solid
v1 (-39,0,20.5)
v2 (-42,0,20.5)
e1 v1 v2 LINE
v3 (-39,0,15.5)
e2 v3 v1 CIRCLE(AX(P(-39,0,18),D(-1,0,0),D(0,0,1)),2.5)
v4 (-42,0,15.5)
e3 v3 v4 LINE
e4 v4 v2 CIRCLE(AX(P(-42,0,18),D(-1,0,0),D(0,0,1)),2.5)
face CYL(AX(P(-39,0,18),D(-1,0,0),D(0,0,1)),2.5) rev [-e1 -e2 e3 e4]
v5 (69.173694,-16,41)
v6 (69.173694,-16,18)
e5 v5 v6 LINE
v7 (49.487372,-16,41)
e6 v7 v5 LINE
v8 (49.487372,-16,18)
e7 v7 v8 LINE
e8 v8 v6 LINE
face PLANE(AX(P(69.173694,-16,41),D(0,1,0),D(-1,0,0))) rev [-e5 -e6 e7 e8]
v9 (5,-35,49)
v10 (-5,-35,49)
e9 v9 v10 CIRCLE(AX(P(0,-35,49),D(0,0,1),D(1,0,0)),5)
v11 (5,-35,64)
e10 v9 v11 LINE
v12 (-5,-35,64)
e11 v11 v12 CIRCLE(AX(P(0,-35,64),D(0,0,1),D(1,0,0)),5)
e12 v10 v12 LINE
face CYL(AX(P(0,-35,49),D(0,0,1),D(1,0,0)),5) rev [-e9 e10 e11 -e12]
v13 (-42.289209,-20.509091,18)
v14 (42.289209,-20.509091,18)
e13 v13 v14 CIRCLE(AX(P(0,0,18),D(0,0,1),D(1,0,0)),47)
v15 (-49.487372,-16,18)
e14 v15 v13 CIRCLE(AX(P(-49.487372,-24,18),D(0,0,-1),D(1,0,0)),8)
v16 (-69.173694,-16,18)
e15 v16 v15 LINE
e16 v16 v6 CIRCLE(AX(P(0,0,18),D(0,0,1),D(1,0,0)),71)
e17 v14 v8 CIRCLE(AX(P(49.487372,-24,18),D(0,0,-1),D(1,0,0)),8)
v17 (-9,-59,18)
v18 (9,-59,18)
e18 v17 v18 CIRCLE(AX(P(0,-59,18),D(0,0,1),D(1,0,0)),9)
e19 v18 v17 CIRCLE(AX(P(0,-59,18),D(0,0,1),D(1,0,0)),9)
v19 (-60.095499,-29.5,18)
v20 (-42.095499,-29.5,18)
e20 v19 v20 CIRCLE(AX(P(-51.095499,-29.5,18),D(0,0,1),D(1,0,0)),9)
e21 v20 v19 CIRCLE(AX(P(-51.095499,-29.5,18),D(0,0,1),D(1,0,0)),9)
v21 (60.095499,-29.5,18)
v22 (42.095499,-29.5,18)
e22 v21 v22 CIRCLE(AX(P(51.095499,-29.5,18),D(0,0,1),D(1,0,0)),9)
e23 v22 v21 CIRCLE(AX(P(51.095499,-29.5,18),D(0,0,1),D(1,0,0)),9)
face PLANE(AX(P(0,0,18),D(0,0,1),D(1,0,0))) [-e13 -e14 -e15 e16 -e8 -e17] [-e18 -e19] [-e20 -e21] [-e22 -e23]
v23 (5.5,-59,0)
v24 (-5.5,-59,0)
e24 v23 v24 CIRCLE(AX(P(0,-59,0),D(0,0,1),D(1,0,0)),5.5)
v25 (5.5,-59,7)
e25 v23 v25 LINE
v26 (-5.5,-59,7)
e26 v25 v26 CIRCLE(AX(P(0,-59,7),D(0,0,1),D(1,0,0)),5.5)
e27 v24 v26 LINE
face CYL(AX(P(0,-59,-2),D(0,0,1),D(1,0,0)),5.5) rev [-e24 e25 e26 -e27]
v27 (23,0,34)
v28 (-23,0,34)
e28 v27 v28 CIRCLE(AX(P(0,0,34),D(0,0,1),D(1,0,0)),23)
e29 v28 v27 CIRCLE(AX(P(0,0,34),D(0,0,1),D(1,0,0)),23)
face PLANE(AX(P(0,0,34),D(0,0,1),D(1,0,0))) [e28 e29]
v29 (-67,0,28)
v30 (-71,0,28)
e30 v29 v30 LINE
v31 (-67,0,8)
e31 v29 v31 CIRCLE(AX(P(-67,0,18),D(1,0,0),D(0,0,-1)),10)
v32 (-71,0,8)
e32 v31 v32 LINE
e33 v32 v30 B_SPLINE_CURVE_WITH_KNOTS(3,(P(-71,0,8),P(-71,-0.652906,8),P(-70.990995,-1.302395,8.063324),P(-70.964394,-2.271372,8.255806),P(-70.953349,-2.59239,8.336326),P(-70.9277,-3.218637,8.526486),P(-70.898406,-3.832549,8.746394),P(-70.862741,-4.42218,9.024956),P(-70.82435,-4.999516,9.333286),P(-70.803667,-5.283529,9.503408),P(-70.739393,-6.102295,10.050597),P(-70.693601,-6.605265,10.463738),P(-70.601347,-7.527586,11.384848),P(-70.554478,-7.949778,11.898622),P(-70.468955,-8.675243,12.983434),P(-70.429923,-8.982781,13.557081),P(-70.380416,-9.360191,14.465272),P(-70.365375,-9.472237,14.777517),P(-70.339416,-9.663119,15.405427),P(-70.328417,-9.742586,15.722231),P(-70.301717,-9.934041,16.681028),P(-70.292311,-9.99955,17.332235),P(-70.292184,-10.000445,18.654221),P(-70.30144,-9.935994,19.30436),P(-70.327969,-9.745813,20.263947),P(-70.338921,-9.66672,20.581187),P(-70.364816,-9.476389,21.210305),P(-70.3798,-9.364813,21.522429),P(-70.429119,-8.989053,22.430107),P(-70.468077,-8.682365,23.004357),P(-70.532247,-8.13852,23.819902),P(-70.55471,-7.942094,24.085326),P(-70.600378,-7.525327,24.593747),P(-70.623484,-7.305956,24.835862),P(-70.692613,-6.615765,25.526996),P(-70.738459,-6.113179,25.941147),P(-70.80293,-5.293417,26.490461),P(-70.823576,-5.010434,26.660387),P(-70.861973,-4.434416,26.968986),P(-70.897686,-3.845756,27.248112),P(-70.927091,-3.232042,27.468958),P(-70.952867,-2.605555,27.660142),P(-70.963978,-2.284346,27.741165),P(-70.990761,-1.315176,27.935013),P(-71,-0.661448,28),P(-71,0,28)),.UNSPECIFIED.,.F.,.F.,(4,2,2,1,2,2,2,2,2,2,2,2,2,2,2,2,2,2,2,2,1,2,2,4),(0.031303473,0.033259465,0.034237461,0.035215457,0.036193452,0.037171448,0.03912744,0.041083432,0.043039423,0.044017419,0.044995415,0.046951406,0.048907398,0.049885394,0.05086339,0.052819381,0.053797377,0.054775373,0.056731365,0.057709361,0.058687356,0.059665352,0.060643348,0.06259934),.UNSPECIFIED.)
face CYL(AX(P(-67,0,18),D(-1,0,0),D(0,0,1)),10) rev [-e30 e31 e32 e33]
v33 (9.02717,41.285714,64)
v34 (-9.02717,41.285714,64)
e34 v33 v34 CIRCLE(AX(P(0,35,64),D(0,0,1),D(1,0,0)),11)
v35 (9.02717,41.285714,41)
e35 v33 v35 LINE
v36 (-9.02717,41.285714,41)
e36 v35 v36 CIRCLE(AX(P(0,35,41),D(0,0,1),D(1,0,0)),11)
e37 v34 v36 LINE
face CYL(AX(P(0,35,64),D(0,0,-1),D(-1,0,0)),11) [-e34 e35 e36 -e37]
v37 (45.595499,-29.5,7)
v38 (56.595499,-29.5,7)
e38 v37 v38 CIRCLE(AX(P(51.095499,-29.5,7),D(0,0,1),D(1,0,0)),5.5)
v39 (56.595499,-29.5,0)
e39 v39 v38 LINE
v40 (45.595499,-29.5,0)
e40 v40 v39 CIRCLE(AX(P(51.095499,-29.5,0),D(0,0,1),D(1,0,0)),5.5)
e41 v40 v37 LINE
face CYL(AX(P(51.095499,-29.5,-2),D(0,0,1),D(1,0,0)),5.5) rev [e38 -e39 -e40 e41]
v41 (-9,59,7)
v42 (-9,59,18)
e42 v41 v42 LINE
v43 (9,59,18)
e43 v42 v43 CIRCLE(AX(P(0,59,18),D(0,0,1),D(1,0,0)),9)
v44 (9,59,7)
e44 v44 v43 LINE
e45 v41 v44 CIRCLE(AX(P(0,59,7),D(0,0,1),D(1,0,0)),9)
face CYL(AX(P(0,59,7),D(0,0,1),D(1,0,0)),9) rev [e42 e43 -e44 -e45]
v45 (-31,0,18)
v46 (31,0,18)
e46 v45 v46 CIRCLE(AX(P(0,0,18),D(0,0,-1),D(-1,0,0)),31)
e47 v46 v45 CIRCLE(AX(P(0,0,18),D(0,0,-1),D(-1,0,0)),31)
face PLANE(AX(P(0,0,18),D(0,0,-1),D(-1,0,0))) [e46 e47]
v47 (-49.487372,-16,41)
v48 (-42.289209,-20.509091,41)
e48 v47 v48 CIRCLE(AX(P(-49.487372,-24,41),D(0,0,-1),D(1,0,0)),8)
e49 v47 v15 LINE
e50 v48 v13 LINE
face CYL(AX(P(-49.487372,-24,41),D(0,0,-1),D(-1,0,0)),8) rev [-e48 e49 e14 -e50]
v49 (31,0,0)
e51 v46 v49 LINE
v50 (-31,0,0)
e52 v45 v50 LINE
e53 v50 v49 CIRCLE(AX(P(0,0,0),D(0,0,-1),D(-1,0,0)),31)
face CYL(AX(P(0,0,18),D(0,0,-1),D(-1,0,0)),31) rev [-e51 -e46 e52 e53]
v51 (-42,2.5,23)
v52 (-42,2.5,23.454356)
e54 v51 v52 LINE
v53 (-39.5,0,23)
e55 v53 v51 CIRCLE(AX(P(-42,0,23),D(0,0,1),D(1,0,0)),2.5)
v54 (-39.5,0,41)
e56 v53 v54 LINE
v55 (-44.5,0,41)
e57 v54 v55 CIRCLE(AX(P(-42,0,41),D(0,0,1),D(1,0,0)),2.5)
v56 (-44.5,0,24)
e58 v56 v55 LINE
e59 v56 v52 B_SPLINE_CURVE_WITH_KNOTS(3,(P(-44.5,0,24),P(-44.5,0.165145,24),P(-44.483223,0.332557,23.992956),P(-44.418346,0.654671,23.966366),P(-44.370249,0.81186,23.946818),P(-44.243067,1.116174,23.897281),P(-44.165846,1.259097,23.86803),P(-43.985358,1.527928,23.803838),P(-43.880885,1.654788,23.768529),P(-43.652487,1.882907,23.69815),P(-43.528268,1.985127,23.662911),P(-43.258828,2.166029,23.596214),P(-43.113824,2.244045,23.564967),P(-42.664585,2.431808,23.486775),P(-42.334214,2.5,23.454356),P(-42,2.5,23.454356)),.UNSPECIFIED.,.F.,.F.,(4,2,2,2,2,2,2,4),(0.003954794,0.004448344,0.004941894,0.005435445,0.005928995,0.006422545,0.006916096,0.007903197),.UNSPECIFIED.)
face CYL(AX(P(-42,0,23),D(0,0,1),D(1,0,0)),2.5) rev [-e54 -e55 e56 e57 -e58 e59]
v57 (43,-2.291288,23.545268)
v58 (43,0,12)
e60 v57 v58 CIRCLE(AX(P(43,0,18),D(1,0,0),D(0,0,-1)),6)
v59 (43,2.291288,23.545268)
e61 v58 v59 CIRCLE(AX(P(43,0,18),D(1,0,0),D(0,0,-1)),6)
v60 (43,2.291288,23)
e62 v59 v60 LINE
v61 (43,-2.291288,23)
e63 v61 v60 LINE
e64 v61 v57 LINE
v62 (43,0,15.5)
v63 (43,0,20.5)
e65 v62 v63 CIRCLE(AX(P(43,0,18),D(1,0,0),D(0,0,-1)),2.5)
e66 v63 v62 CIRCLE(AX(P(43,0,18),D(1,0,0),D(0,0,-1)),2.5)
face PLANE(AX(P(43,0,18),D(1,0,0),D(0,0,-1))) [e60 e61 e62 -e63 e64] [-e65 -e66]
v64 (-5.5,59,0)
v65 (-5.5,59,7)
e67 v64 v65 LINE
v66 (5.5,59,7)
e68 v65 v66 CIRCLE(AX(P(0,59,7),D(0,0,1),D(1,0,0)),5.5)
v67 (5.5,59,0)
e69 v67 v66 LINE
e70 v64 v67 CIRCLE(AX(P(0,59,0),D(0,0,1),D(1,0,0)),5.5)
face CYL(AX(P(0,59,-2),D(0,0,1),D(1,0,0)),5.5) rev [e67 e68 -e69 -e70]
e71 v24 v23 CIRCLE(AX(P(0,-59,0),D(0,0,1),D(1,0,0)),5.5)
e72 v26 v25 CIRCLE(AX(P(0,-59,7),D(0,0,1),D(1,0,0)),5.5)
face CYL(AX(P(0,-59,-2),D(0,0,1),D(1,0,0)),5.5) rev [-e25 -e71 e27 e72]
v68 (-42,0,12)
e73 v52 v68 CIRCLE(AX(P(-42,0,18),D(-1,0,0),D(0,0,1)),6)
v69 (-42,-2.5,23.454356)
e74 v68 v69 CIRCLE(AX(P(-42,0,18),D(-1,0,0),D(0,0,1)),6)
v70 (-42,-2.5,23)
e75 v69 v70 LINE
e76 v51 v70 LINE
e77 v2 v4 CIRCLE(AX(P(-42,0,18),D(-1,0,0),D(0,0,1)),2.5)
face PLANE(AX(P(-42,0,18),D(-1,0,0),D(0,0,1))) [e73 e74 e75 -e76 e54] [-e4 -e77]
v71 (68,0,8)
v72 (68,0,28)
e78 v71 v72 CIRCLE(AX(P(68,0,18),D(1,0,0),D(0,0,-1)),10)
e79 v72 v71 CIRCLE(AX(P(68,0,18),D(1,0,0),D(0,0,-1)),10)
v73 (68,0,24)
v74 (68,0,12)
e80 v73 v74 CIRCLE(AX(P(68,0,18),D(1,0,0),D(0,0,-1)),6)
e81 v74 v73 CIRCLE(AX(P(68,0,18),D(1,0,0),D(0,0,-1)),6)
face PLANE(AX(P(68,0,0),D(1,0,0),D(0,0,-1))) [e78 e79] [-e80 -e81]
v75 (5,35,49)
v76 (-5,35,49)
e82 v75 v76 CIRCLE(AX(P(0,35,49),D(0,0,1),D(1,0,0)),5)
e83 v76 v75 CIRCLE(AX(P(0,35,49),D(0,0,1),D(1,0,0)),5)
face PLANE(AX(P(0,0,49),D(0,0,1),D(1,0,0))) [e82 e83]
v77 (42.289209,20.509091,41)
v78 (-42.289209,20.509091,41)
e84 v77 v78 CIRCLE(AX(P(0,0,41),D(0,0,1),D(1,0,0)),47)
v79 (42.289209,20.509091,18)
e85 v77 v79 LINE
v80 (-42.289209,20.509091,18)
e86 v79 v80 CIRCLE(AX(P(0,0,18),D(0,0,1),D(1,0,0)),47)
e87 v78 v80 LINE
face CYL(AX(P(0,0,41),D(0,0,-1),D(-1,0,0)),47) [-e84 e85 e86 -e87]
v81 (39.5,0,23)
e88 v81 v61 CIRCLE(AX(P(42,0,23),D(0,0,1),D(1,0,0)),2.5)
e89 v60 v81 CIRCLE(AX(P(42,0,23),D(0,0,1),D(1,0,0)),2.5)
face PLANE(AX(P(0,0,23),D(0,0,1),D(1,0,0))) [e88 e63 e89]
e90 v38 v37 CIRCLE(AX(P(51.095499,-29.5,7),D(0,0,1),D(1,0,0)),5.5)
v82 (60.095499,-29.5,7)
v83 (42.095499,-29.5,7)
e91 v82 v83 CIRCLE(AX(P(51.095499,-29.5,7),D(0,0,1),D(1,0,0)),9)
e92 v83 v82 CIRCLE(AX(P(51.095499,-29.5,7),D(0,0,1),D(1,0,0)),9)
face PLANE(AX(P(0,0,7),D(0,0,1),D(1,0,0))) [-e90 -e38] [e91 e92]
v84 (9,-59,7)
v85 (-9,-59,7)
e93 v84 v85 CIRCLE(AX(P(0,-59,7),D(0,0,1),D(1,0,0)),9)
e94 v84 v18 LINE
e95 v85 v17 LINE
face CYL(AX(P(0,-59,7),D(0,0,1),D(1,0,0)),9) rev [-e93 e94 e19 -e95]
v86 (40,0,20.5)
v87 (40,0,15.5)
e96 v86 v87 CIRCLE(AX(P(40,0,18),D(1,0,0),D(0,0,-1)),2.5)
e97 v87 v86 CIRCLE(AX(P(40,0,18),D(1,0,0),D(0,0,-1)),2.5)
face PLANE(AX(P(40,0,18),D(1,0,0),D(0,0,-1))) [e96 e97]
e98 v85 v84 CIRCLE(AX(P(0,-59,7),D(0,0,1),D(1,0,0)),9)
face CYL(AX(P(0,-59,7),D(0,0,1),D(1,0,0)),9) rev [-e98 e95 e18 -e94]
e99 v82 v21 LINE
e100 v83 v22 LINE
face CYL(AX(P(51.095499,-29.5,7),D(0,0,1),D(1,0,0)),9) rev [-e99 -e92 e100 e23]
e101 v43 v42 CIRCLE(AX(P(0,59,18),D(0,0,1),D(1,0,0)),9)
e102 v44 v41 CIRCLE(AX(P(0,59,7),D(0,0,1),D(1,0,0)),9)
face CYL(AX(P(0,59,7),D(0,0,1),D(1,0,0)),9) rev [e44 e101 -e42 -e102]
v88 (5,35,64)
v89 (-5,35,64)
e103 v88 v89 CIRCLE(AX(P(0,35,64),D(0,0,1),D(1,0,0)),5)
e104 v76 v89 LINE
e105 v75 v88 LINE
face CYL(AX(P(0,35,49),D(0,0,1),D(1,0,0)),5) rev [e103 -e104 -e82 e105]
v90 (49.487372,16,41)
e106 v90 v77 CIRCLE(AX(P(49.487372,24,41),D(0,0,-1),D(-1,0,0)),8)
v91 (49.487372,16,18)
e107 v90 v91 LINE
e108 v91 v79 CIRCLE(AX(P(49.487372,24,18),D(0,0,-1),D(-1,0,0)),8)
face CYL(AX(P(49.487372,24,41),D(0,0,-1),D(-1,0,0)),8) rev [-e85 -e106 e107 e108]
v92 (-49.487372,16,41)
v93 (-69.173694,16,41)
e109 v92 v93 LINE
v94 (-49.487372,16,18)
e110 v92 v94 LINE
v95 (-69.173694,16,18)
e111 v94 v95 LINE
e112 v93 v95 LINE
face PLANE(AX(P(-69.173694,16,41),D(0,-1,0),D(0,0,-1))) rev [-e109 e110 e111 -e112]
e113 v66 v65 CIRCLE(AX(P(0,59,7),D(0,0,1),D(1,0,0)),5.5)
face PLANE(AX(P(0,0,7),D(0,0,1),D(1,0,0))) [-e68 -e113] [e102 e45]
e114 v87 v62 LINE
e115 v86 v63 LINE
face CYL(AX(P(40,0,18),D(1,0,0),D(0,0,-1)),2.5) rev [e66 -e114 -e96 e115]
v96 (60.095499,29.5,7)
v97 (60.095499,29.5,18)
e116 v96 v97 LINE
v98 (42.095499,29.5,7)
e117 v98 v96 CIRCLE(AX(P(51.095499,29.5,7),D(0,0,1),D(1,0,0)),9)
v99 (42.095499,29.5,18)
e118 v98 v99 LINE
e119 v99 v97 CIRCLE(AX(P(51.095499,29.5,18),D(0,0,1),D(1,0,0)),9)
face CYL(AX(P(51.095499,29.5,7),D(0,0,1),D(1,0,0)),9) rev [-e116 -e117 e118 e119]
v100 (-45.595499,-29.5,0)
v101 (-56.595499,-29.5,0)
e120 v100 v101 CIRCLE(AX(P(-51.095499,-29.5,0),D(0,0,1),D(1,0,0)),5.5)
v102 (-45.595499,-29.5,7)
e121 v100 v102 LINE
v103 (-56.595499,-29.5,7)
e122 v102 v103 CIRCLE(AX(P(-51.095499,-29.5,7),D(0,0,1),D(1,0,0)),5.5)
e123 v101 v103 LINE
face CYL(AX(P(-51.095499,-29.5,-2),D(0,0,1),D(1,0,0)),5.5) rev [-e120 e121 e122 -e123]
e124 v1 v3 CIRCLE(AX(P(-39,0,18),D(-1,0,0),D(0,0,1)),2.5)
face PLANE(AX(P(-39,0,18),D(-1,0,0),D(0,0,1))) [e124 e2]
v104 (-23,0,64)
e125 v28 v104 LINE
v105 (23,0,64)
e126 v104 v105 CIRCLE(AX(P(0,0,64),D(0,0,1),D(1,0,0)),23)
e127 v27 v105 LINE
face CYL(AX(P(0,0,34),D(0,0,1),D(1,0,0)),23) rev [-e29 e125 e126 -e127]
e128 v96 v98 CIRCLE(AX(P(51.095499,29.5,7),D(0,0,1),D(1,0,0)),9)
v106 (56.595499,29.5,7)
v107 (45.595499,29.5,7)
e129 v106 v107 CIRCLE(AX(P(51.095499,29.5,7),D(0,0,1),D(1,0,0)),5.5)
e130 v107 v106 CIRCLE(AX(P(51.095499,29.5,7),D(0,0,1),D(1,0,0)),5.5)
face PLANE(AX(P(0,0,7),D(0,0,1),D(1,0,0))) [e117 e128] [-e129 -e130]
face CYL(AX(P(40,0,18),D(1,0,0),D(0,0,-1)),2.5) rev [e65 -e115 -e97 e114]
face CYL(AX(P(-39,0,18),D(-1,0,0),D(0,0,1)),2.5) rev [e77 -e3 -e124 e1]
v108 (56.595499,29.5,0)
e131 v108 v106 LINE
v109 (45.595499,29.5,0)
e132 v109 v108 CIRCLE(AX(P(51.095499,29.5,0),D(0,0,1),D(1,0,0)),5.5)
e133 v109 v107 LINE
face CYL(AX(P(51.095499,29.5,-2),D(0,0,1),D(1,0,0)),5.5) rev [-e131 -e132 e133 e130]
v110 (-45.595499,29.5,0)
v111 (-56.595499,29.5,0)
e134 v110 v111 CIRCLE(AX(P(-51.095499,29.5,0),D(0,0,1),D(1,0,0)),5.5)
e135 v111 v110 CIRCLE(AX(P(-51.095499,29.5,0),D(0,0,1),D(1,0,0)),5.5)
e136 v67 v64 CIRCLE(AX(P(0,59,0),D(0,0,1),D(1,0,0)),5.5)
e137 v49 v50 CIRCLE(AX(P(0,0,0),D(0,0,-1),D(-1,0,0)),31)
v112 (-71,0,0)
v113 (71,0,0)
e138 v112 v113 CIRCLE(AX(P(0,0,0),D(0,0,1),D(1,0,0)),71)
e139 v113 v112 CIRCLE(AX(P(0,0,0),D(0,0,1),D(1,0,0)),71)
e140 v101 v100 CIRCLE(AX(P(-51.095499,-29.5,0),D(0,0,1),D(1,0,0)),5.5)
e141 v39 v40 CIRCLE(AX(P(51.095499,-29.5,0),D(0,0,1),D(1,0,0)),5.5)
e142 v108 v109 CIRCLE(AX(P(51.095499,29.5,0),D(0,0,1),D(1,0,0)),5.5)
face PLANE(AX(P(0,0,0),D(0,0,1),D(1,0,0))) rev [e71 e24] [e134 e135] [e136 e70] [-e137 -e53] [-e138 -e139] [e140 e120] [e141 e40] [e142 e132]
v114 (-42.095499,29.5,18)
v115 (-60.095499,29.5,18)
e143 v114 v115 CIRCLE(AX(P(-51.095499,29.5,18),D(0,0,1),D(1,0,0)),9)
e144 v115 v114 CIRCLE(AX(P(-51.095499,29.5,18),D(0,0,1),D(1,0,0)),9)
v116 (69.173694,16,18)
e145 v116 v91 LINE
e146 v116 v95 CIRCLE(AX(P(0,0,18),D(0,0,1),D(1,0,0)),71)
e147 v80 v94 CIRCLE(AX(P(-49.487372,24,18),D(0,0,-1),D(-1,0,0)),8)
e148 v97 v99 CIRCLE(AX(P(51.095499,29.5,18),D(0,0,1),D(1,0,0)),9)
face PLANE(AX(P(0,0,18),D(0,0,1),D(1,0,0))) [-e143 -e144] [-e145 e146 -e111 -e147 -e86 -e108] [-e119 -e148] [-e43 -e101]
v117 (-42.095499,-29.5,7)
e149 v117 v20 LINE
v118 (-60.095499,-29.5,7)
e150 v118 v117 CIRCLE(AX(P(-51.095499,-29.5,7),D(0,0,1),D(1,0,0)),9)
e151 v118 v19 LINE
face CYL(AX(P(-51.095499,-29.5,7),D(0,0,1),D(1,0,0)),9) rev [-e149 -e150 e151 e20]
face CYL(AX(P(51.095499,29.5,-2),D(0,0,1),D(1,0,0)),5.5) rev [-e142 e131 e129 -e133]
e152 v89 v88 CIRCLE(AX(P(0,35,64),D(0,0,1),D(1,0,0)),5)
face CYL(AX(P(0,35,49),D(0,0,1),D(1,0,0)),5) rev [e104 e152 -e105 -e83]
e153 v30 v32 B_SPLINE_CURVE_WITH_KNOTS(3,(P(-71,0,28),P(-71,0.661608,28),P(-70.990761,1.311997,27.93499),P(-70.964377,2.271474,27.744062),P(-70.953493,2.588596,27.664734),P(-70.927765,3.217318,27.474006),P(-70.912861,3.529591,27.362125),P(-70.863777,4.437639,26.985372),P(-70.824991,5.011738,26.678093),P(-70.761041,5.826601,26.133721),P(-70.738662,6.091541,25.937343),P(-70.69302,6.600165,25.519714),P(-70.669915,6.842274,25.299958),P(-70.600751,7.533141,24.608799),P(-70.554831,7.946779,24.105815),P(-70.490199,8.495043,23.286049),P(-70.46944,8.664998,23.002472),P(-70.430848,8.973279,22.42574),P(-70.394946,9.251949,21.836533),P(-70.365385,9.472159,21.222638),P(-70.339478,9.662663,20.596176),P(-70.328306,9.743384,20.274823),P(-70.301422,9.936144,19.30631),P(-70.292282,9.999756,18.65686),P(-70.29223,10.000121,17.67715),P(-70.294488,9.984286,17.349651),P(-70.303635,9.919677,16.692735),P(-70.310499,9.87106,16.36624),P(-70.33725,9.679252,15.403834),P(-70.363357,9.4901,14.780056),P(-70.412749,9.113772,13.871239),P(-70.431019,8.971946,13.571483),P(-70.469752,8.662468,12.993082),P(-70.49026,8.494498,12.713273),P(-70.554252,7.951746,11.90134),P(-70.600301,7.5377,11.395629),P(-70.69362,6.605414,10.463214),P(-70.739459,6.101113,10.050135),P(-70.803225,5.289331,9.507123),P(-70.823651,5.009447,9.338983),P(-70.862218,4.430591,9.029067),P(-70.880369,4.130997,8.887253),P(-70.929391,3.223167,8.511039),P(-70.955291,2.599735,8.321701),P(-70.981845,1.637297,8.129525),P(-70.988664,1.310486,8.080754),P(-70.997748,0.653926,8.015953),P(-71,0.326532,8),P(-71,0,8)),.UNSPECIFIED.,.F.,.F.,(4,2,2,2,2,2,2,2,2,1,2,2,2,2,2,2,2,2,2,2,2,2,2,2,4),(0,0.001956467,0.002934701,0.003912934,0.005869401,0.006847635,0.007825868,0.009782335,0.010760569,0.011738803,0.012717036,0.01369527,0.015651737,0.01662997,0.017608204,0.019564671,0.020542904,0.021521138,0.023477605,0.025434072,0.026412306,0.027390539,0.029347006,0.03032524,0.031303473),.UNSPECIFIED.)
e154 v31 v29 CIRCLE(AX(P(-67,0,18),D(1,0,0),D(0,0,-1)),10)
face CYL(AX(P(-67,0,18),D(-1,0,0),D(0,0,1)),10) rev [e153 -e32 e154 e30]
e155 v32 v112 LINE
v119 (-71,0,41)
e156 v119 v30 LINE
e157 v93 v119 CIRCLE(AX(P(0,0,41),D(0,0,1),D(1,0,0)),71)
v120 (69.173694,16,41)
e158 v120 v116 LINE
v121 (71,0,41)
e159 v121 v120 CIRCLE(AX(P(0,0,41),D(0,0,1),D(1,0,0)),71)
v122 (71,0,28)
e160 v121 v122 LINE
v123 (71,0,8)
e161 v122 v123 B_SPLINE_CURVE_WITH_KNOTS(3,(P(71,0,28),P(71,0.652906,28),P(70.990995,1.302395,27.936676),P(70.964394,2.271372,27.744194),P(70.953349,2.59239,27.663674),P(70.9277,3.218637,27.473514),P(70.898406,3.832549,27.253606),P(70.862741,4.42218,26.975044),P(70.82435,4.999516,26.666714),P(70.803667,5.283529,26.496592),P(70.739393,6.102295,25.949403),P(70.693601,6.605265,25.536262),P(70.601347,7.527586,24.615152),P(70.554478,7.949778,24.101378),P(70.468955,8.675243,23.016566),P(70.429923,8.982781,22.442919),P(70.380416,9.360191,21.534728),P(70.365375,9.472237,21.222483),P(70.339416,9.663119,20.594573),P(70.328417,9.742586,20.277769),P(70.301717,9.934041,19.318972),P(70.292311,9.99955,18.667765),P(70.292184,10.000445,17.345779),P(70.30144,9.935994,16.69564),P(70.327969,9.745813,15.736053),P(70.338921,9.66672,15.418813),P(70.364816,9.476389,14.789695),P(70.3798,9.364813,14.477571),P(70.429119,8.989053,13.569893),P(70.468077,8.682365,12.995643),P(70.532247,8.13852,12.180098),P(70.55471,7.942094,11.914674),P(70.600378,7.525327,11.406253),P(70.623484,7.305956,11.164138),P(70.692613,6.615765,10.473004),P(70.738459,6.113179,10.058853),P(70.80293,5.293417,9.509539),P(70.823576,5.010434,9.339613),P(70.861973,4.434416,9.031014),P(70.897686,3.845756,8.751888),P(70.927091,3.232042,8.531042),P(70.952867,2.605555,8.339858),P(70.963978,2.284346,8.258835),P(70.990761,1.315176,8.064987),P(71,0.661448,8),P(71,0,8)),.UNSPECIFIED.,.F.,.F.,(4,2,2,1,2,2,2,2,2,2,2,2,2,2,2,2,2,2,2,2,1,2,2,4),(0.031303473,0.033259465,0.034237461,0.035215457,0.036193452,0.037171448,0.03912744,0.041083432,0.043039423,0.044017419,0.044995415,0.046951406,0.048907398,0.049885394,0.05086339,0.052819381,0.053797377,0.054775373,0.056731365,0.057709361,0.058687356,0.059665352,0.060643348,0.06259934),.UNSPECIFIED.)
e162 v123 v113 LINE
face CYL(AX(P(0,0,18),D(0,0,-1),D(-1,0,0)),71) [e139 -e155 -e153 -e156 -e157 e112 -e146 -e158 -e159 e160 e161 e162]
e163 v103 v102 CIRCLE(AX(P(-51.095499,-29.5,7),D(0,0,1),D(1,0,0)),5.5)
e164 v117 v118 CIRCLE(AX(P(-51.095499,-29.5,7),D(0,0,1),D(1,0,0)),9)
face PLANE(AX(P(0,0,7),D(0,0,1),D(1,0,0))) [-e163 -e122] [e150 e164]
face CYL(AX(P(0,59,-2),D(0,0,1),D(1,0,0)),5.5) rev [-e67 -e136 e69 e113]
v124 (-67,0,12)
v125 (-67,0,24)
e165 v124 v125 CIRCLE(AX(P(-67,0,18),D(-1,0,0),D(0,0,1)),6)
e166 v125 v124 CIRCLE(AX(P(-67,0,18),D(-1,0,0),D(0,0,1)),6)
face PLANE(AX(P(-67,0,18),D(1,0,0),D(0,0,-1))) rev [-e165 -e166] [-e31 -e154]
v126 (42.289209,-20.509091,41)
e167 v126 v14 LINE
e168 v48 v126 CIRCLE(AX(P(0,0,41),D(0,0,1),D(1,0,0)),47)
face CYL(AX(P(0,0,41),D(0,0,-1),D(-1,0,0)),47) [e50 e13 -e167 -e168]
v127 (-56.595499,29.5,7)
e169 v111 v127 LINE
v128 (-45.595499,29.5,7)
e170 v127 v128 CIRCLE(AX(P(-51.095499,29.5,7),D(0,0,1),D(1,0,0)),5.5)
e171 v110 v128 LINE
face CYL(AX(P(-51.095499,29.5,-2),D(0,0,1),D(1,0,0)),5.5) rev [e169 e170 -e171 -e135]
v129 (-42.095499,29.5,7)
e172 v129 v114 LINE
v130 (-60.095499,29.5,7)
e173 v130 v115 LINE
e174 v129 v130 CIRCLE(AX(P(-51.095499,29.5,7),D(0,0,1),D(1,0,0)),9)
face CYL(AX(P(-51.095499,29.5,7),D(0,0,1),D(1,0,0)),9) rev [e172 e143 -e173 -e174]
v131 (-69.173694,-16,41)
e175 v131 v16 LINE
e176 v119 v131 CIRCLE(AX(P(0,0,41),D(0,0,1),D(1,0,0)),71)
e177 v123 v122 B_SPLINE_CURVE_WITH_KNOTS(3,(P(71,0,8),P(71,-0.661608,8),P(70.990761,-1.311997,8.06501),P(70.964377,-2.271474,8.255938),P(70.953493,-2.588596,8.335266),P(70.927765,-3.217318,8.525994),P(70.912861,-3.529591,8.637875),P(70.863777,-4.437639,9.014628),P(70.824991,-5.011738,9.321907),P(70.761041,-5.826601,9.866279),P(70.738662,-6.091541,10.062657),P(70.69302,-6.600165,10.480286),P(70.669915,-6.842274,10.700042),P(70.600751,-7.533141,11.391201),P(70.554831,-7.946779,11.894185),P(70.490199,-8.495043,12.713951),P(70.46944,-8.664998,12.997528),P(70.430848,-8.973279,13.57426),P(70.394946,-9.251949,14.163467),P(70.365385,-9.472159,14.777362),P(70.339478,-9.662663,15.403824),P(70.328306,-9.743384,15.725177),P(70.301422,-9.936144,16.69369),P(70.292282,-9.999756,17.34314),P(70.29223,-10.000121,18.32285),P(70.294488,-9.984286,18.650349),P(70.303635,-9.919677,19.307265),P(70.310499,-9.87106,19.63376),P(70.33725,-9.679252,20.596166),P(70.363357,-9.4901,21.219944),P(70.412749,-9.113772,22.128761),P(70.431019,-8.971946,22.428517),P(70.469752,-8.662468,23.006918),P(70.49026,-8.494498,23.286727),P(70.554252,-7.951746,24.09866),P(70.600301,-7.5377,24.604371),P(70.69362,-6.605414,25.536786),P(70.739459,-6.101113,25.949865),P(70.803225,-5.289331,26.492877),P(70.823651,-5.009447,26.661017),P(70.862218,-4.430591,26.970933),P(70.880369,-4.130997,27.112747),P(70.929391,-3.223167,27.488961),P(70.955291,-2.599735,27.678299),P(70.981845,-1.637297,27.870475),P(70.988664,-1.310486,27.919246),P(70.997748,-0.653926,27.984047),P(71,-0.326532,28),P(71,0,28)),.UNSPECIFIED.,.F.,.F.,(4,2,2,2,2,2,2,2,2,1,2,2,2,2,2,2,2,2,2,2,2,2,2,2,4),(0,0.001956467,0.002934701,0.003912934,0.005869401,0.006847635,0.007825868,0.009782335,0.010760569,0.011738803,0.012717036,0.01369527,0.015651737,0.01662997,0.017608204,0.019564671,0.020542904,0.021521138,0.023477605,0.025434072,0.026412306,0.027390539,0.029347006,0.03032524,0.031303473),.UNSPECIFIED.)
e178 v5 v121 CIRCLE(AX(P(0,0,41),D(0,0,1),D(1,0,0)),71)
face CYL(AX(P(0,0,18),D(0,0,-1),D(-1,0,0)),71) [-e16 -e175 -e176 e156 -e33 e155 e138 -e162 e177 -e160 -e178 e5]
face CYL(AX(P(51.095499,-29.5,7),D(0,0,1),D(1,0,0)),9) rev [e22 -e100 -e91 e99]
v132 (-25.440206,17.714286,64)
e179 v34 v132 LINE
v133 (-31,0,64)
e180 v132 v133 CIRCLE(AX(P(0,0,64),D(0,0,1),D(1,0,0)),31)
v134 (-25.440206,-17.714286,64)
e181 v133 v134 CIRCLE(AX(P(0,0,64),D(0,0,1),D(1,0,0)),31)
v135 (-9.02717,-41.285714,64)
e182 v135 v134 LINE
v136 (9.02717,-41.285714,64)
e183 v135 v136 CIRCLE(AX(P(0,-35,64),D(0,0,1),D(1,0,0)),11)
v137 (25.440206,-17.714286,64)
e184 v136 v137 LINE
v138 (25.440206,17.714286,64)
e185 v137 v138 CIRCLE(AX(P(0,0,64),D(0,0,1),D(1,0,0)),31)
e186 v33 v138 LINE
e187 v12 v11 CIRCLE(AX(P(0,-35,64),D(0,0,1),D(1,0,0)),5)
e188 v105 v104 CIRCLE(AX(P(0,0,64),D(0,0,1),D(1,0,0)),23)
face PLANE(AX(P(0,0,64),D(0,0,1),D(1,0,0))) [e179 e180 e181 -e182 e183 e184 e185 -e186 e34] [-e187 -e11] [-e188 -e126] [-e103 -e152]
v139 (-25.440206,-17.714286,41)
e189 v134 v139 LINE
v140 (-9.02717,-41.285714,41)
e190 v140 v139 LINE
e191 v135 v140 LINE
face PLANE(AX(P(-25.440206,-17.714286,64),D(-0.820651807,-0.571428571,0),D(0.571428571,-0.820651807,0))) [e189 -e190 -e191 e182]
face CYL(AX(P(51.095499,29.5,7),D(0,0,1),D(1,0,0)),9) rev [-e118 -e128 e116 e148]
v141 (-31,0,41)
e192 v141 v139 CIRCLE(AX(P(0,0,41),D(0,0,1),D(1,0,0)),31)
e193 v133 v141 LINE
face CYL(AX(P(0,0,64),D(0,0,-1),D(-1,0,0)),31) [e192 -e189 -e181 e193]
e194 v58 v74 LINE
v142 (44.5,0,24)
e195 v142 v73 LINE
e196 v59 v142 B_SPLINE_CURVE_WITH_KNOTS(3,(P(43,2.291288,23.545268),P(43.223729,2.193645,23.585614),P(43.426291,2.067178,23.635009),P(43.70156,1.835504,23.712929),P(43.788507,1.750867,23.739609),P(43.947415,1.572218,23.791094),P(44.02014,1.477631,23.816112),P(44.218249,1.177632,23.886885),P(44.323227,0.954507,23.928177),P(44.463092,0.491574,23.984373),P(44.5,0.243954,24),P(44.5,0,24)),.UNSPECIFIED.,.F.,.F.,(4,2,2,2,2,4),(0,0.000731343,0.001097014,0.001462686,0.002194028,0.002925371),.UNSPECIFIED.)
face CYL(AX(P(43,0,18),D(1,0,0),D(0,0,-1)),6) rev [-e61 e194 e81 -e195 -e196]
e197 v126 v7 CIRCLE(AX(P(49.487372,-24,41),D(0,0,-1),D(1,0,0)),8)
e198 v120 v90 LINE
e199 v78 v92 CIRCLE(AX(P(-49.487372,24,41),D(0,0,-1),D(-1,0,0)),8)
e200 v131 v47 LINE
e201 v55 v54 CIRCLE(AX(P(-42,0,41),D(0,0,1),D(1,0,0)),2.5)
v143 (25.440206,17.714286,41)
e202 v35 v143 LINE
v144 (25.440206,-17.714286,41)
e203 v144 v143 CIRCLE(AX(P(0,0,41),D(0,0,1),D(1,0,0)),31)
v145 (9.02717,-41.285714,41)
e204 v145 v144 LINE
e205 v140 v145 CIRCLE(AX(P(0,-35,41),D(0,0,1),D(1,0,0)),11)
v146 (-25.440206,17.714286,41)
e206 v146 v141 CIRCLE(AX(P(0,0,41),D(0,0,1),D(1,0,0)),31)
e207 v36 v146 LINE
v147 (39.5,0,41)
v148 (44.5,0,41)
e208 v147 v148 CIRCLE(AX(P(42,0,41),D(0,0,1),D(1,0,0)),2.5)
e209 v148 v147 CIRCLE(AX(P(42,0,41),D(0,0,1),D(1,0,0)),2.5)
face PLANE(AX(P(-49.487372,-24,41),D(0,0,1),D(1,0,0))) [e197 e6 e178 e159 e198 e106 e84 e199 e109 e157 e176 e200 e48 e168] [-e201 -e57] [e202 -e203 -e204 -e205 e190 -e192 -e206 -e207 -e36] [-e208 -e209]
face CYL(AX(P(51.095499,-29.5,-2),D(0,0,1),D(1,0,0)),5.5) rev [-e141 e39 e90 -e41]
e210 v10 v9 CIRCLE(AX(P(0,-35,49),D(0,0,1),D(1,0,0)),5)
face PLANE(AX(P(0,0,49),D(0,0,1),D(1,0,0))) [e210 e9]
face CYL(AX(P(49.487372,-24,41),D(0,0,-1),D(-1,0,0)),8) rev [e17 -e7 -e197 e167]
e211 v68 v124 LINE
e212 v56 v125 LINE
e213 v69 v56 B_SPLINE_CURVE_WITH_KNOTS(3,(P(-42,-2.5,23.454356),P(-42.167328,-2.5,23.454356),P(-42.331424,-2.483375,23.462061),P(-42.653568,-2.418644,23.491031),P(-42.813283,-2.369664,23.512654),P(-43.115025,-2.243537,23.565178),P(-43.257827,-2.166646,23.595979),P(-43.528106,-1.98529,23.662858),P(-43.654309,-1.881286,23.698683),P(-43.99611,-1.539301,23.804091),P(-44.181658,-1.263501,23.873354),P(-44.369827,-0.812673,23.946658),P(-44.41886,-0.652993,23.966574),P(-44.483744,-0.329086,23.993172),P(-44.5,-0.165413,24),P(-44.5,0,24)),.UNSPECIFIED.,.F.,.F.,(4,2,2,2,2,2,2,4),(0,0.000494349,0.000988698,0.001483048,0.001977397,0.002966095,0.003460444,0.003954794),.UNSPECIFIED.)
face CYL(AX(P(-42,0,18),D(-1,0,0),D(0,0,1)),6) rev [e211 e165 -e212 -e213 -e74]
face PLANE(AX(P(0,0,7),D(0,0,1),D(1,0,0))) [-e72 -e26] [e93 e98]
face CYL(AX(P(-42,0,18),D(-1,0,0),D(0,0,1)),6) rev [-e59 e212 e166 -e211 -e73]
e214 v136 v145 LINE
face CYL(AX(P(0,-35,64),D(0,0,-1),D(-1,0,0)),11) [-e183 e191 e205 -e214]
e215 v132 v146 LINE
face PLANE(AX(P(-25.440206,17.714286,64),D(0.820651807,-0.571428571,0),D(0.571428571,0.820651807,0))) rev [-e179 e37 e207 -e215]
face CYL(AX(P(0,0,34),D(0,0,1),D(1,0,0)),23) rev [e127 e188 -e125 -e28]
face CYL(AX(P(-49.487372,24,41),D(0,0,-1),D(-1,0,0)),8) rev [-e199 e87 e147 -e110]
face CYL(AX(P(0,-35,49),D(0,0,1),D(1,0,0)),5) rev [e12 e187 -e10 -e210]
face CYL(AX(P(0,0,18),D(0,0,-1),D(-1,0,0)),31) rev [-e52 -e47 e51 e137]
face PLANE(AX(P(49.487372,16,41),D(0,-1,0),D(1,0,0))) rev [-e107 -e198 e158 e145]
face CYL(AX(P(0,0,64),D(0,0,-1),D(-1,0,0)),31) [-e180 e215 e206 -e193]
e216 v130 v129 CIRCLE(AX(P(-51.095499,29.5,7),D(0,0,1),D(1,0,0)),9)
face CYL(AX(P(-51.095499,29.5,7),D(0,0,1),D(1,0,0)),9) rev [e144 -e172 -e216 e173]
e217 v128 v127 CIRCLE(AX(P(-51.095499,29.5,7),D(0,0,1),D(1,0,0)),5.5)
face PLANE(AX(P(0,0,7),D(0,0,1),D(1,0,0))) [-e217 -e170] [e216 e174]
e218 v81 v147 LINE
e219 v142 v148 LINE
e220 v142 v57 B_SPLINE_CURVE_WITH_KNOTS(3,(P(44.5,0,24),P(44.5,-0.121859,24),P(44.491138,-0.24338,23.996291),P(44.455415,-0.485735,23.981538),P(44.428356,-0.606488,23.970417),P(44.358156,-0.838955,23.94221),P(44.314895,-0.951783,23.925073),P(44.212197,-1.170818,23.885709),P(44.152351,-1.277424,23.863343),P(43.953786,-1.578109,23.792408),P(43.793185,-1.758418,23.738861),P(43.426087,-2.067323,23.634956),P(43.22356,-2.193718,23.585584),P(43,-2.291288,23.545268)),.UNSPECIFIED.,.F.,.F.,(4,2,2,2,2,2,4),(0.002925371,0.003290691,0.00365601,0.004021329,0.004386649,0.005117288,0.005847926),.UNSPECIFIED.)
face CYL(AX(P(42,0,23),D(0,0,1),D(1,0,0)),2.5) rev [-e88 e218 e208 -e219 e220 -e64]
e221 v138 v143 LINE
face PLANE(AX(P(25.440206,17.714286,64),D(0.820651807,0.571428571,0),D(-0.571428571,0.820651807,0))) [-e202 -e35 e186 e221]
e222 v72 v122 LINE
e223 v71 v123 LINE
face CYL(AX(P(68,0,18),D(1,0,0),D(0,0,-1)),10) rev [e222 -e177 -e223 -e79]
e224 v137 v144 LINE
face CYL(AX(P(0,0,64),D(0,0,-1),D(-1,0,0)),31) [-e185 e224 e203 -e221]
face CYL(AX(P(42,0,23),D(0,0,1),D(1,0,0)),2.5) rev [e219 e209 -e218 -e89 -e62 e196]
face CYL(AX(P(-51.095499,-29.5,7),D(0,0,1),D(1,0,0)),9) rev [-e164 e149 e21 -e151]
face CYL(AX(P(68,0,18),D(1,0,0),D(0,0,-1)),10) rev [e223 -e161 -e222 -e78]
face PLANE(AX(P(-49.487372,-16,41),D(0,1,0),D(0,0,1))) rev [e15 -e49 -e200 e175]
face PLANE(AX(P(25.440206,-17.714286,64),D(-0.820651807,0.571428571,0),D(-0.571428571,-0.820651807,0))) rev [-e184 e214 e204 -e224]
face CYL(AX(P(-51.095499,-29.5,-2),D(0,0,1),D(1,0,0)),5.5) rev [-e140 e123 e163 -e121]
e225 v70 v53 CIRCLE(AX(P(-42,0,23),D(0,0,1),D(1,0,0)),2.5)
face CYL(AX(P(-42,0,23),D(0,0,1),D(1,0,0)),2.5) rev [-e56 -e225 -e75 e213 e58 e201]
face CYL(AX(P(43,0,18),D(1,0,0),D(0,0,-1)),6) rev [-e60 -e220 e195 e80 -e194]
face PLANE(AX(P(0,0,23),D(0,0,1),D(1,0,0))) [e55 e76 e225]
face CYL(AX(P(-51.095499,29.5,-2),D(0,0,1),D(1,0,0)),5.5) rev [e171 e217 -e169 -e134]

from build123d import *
from build123d.topology import SkipClean

# Parameters (mm, degrees)
FLANGE_SKETCH_R              = 71
FLANGE_142_DEPTH             = 18
BODY_BOSS_WITH_LUGS_DEPTH    = 23
FLANGE_COUNTERBORE_SKETCH_R  = 9
FLANGE_COUNTERBORES_6X_DEPTH = 11
FLANGE_HOLE_SKETCH_R         = 5.5
FLANGE_HOLES_6X_11_DEPTH     = 20
TOP_BOSS_DEPTH               = 23
BORE_SKETCH_R                = 23
BORE_46_DEPTH                = 30
TOP_BOSS_HOLE_SKETCH_R       = 5
TOP_BOSS_HOLES_DEPTH         = 15
THROUGH_BORE_SKETCH_R        = 31
THROUGH_BORE_62_DEPTH        = 18
BODY_BOSS_HOLE_SKETCH_R      = 2.5
BODY_BOSS_HOLES_DEPTH        = 18
LUG_A_SPOT_FACE_DEPTH        = 4
LUG_A_HOLE_12_SKETCH_R       = 6
LUG_A_HOLE_12_DEPTH          = 25
LUG_A_HOLE_5_SKETCH_R        = 2.5
LUG_A_HOLE_5_DEPTH           = 3
LUG_START                    = 4
LUG_B_SPOT_FACE_SKETCH_R     = 10
LUG_B_SPOT_FACE_DEPTH        = 4
LUG_START_2                  = -25
LUG_B_HOLE_12_SKETCH_R       = 6
LUG_B_HOLE_12_DEPTH          = 25
LUG_START_3                  = -3
LUG_B_HOLE_5_SKETCH_R        = 2.5
LUG_B_HOLE_5_DEPTH           = 3


with BuildPart() as part:
    # Flange Sketch → Flange Ø142 (new body)
    with BuildSketch(Plane.XY):
        Circle(FLANGE_SKETCH_R)
    extrude(amount=FLANGE_142_DEPTH)

    # Body Boss Sketch → Body Boss With Lugs (add)
    with SkipClean():  # the faces are left unmerged after this step: merging them gives an invalid solid
        with BuildSketch(Plane.XY.offset(18)):
            with BuildLine():
                Line((-69.173694422, 16), (-49.487372127, 16))
                ThreePointArc((-49.487372127, 16), (-45.240448106, 17.22035131), (-42.289208908, 20.509090909))
                ThreePointArc((-42.289208908, 20.509090909), (0, 47), (42.289208908, 20.509090909))
                ThreePointArc((42.289208908, 20.509090909), (45.240448106, 17.22035131), (49.487372127, 16))
                Line((49.487372127, 16), (69.173694422, 16))
                ThreePointArc((69.173694422, 16), (71, 0), (69.173694422, -16))
                Line((69.173694422, -16), (49.487372127, -16))
                ThreePointArc((49.487372127, -16), (45.240448106, -17.22035131), (42.289208908, -20.509090909))
                ThreePointArc((42.289208908, -20.509090909), (0, -47), (-42.289208908, -20.509090909))
                ThreePointArc((-42.289208908, -20.509090909), (-45.240448106, -17.22035131), (-49.487372127, -16))
                Line((-49.487372127, -16), (-69.173694422, -16))
                ThreePointArc((-69.173694422, -16), (-71, 0), (-69.173694422, 16))
            make_face()
        extrude(amount=BODY_BOSS_WITH_LUGS_DEPTH)

    # Flange Counterbore Sketch → Flange Counterbores 6x (cut)
    with SkipClean():  # the faces are left unmerged after this step: merging them gives an invalid solid
        with BuildSketch(Plane.XY.offset(18)):
            with Locations((0, 59)):
                Circle(FLANGE_COUNTERBORE_SKETCH_R)
            with Locations((51.095498823, 29.5)):
                Circle(FLANGE_COUNTERBORE_SKETCH_R)
            with Locations((51.095498823, -29.5)):
                Circle(FLANGE_COUNTERBORE_SKETCH_R)
            with Locations((0, -59)):
                Circle(FLANGE_COUNTERBORE_SKETCH_R)
            with Locations((-51.095498823, -29.5)):
                Circle(FLANGE_COUNTERBORE_SKETCH_R)
            with Locations((-51.095498823, 29.5)):
                Circle(FLANGE_COUNTERBORE_SKETCH_R)
        extrude(amount=-FLANGE_COUNTERBORES_6X_DEPTH, mode=Mode.SUBTRACT)

    # Flange Hole Sketch → Flange Holes 6xØ11 (cut)
    with SkipClean():  # the faces are left unmerged after this step: merging them gives an invalid solid
        with BuildSketch(Plane.XY.offset(18)):
            with Locations((0, 59)):
                Circle(FLANGE_HOLE_SKETCH_R)
            with Locations((51.095498823, 29.5)):
                Circle(FLANGE_HOLE_SKETCH_R)
            with Locations((51.095498823, -29.5)):
                Circle(FLANGE_HOLE_SKETCH_R)
            with Locations((0, -59)):
                Circle(FLANGE_HOLE_SKETCH_R)
            with Locations((-51.095498823, -29.5)):
                Circle(FLANGE_HOLE_SKETCH_R)
            with Locations((-51.095498823, 29.5)):
                Circle(FLANGE_HOLE_SKETCH_R)
        extrude(amount=-FLANGE_HOLES_6X_11_DEPTH, mode=Mode.SUBTRACT)

    # Top Boss Sketch → Top Boss (add)
    with SkipClean():  # the faces are left unmerged after this step: merging them gives an invalid solid
        with BuildSketch(Plane.XY.offset(41)):
            with BuildLine():
                Line((9.027169873, -41.285714286), (25.440206006, -17.714285714))
                ThreePointArc((25.440206006, -17.714285714), (31, 0), (25.440206006, 17.714285714))
                Line((25.440206006, 17.714285714), (9.027169873, 41.285714286))
                ThreePointArc((9.027169873, 41.285714286), (0, 46), (-9.027169873, 41.285714286))
                Line((-9.027169873, 41.285714286), (-25.440206006, 17.714285714))
                ThreePointArc((-25.440206006, 17.714285714), (-31, 0), (-25.440206006, -17.714285714))
                Line((-25.440206006, -17.714285714), (-9.027169873, -41.285714286))
                ThreePointArc((-9.027169873, -41.285714286), (0, -46), (9.027169873, -41.285714286))
            make_face()
        extrude(amount=TOP_BOSS_DEPTH)

    # Bore Sketch → Bore Ø46 (cut)
    with SkipClean():  # the faces are left unmerged after this step: merging them gives an invalid solid
        with BuildSketch(Plane.XY.offset(64)):
            Circle(BORE_SKETCH_R)
        extrude(amount=-BORE_46_DEPTH, mode=Mode.SUBTRACT)

    # Top Boss Hole Sketch → Top Boss Holes (cut)
    with SkipClean():  # the faces are left unmerged after this step: merging them gives an invalid solid
        with BuildSketch(Plane.XY.offset(64)):
            with Locations((0, 35)):
                Circle(TOP_BOSS_HOLE_SKETCH_R)
            with Locations((0, -35)):
                Circle(TOP_BOSS_HOLE_SKETCH_R)
        extrude(amount=-TOP_BOSS_HOLES_DEPTH, mode=Mode.SUBTRACT)

    # Through Bore Sketch → Through Bore Ø62 (cut)
    with SkipClean():  # the faces are left unmerged after this step: merging them gives an invalid solid
        with BuildSketch(Plane(origin=(0, 0, 0), x_dir=(-1, 0, 0), z_dir=(0, 0, -1))):
            Circle(THROUGH_BORE_SKETCH_R)
        extrude(amount=-THROUGH_BORE_62_DEPTH, mode=Mode.SUBTRACT)

    # Body Boss Hole Sketch → Body Boss Holes (cut)
    with SkipClean():  # the faces are left unmerged after this step: merging them gives an invalid solid
        with BuildSketch(Plane.XY.offset(41)):
            with Locations((-42, 0)):
                Circle(BODY_BOSS_HOLE_SKETCH_R)
            with Locations((42, 0)):
                Circle(BODY_BOSS_HOLE_SKETCH_R)
        extrude(amount=-BODY_BOSS_HOLES_DEPTH, mode=Mode.SUBTRACT)

    # Lug A Spot Face Sketch → Lug A Spot Face (cut)
    with SkipClean():  # the faces are left unmerged after this step: merging them gives an invalid solid
        with BuildSketch(Plane(origin=(72, 0, 0), x_dir=(0, 0, -1), z_dir=(1, 0, 0))):
            with BuildLine():
                ThreePointArc((-8, 0), (-10.928932188, 7.071067812), (-18, 10))
                Line((-18, 10), (-18, -10))
                ThreePointArc((-18, -10), (-10.928932188, -7.071067812), (-8, 0))
            make_face()
            with BuildLine():
                Line((-18, -10), (-18, 10))
                ThreePointArc((-18, 10), (-28, 0), (-18, -10))
            make_face()
        extrude(amount=-LUG_A_SPOT_FACE_DEPTH, mode=Mode.SUBTRACT)

    # Lug A Hole Ø12 Sketch → Lug A Hole Ø12 (cut)
    with SkipClean():  # the faces are left unmerged after this step: merging them gives an invalid solid
        with BuildSketch(Plane(origin=(68, 0, 0), x_dir=(0, 0, -1), z_dir=(1, 0, 0))):
            with Locations((-18, 0)):
                Circle(LUG_A_HOLE_12_SKETCH_R)
        extrude(amount=-LUG_A_HOLE_12_DEPTH, mode=Mode.SUBTRACT)

    # Lug A Hole Ø5 Sketch → Lug A Hole Ø5 (cut)
    with SkipClean():  # the faces are left unmerged after this step: merging them gives an invalid solid
        with BuildSketch(Plane(origin=(43, 0, 0), x_dir=(0, 0, -1), z_dir=(1, 0, 0))):
            with Locations((-18, 0)):
                Circle(LUG_A_HOLE_5_SKETCH_R)
        extrude(amount=-LUG_A_HOLE_5_DEPTH, mode=Mode.SUBTRACT)

    # Lug B Spot Face Sketch → Lug B Spot Face (cut)
    with SkipClean():  # the faces are left unmerged after this step: merging them gives an invalid solid
        with BuildSketch(Plane(origin=(-71, 0, 0), x_dir=(0, 0, -1), z_dir=(1, 0, 0)).offset(LUG_START)):
            with Locations((-18, 0)):
                Circle(LUG_B_SPOT_FACE_SKETCH_R)
        extrude(amount=-LUG_B_SPOT_FACE_DEPTH, mode=Mode.SUBTRACT)

    # Lug B Hole Ø12 Sketch → Lug B Hole Ø12 (cut)
    with SkipClean():  # the faces are left unmerged after this step: merging them gives an invalid solid
        with BuildSketch(Plane.ZY.offset(67).offset(LUG_START_2)):
            with Locations(Location((18, 0, 0), (0, 0, 180))):
                Circle(LUG_B_HOLE_12_SKETCH_R)
        extrude(amount=LUG_B_HOLE_12_DEPTH, mode=Mode.SUBTRACT)

    # Lug B Hole Ø5 Sketch → Lug B Hole Ø5 (cut)
    with SkipClean():  # the faces are left unmerged after this step: merging them gives an invalid solid
        with BuildSketch(Plane.ZY.offset(42).offset(LUG_START_3)):
            with Locations(Location((18, 0, 0), (0, 0, 180))):
                Circle(LUG_B_HOLE_5_SKETCH_R)
        extrude(amount=LUG_B_HOLE_5_DEPTH, mode=Mode.SUBTRACT)


solid = part.part
